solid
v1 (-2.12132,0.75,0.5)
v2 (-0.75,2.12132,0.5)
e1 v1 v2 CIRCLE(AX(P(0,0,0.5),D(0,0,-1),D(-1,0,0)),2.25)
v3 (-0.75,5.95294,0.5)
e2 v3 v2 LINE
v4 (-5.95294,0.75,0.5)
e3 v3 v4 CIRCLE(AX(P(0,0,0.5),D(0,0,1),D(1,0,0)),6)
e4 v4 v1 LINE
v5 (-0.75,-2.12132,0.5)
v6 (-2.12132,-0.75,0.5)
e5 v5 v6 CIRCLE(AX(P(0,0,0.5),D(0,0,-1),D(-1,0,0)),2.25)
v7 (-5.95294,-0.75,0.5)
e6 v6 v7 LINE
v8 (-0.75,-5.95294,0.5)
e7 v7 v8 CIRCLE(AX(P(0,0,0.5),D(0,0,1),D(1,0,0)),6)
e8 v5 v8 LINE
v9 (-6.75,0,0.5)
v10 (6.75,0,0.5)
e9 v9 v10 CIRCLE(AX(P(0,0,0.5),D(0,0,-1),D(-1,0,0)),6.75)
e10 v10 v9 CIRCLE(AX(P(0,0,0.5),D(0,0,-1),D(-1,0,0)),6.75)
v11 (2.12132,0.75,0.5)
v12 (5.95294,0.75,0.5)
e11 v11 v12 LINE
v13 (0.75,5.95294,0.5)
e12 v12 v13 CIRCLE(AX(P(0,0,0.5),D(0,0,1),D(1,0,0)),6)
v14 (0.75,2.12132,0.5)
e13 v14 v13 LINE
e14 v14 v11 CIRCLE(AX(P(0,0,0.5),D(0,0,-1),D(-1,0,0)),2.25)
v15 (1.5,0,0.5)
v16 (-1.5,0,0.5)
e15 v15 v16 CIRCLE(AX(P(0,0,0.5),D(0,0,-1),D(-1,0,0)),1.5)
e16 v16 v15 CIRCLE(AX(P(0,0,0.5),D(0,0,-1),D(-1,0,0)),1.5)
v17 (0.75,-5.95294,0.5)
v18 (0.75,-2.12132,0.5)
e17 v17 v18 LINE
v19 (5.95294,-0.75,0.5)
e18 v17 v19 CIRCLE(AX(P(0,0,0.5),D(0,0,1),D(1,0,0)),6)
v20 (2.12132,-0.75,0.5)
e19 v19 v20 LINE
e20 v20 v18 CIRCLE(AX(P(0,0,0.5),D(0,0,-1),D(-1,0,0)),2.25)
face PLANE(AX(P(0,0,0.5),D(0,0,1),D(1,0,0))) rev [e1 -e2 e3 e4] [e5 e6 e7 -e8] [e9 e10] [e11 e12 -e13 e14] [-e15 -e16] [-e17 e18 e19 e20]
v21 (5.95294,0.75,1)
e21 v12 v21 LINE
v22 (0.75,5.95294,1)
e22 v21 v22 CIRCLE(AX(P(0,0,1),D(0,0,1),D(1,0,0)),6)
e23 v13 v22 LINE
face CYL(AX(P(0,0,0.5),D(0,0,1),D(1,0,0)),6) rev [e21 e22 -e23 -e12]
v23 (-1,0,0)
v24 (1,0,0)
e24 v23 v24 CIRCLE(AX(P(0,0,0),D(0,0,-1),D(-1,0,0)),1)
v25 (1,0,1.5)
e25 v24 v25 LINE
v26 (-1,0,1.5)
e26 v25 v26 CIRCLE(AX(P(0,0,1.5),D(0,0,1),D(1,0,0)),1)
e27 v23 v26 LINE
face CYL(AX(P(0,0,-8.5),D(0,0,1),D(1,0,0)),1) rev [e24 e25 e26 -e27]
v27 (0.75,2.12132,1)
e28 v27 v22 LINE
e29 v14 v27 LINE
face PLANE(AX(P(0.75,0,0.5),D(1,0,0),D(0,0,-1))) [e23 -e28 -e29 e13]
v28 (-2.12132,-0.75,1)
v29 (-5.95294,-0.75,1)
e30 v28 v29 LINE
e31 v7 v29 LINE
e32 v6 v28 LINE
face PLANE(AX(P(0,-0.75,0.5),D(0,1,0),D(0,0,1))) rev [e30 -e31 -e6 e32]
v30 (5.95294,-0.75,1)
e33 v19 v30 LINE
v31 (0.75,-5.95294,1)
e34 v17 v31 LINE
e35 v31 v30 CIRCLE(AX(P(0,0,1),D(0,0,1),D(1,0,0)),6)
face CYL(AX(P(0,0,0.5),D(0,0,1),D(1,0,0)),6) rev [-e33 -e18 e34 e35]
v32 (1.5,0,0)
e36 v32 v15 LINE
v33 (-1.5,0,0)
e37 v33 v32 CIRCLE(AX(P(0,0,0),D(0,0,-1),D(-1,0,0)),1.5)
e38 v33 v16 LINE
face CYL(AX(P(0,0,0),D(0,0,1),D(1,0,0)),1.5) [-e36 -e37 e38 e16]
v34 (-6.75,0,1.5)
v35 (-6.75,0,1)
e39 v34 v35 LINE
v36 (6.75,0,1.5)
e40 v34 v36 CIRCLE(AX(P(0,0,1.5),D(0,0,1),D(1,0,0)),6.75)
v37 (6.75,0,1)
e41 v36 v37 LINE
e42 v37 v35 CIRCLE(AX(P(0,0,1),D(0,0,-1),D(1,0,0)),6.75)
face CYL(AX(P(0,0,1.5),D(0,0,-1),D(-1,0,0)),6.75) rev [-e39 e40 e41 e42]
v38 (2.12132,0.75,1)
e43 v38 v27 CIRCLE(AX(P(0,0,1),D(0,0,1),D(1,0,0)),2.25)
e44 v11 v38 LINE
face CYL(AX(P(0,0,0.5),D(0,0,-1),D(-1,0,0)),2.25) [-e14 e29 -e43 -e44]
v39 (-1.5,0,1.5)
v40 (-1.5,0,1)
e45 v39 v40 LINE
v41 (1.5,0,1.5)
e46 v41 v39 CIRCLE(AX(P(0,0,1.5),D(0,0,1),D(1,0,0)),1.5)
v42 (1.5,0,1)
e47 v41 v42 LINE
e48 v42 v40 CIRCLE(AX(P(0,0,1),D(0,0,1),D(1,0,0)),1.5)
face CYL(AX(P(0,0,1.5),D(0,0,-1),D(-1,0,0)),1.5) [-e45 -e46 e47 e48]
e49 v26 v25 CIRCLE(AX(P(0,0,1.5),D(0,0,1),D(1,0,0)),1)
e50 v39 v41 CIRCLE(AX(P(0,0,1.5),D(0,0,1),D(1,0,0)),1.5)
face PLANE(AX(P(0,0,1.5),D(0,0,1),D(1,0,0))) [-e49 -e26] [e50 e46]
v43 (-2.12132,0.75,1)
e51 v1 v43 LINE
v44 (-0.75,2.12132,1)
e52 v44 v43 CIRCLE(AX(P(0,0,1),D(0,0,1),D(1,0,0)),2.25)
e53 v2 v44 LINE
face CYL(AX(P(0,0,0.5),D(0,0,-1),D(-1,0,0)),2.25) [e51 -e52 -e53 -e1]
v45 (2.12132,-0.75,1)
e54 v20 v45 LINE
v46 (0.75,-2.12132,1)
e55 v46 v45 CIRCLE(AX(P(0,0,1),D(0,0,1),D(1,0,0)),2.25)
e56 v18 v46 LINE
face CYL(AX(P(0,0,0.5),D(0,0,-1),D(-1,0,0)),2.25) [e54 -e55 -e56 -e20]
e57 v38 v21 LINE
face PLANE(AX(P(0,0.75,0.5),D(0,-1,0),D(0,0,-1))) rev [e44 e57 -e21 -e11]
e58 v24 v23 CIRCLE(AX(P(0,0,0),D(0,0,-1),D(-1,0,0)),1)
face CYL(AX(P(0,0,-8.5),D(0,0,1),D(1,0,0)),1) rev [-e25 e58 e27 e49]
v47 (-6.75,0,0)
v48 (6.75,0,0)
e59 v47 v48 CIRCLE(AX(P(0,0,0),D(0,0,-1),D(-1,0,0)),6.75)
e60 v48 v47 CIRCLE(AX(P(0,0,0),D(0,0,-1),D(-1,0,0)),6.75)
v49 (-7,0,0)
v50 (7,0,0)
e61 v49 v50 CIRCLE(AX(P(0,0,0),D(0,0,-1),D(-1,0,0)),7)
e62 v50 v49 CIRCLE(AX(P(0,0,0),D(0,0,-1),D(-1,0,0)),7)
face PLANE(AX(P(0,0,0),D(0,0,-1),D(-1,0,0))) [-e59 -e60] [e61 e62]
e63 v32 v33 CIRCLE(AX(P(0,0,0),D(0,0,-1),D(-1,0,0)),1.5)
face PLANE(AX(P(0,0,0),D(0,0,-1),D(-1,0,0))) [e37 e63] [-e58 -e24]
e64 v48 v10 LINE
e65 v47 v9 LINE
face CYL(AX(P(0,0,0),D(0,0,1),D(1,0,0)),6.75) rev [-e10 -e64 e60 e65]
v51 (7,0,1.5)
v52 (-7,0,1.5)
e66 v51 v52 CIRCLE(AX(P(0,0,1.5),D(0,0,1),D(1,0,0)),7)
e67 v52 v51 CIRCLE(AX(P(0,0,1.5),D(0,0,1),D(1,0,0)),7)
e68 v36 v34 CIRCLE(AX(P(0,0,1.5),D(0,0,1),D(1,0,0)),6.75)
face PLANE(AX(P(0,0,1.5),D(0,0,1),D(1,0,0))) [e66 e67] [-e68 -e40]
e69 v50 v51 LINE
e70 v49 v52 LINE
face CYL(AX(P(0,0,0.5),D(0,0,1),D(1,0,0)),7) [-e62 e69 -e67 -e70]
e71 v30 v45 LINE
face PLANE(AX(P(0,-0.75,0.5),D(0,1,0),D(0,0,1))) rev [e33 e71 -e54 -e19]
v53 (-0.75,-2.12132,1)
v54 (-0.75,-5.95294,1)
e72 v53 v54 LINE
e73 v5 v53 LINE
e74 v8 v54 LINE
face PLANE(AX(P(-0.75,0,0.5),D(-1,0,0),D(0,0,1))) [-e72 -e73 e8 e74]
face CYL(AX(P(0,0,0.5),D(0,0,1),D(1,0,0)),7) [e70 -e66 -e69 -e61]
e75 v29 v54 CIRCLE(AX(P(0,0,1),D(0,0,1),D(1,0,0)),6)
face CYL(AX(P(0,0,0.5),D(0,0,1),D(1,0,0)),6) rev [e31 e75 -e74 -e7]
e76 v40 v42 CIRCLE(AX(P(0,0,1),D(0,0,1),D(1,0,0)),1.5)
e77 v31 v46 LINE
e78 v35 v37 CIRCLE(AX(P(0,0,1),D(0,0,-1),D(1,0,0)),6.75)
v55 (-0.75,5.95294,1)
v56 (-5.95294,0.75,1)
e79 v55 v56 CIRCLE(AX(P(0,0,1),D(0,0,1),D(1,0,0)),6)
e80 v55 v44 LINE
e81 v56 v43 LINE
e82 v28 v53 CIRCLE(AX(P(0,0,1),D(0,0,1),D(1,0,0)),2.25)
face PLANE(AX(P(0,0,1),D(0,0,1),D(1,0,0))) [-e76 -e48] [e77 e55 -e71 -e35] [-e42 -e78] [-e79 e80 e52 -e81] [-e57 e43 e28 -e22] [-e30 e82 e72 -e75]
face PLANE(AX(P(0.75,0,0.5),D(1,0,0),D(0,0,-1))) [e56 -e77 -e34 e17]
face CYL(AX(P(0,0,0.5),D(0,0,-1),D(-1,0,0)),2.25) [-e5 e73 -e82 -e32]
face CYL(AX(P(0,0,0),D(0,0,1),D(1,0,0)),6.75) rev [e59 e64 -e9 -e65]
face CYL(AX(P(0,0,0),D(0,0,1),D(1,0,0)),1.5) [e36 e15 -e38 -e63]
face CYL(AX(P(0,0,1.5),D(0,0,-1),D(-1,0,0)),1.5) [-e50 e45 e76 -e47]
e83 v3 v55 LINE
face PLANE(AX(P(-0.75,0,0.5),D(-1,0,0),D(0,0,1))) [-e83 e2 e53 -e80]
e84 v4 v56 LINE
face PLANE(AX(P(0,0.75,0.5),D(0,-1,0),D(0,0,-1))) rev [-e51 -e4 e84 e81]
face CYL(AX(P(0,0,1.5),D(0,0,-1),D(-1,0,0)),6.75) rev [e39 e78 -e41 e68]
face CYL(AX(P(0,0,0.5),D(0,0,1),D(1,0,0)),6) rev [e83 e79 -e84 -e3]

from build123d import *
from build123d.topology import SkipClean

# Parameters (mm, degrees)
HUB_CORE_SKETCH_R           = 2.25
HUB_CORE_DEPTH              = 0.5
HUB_FLANGE_SKETCH_R         = 6
HUB_FLANGE_6_DEPTH          = 0.5
FRONT_HUB_BOSS_SKETCH_R     = 2.25
FRONT_HUB_BOSS_DEPTH        = 0.5
CROSS_START                 = -0.5
CROSS_SLOT_CUT_DEPTH        = 0.5
WEB_START                   = -0.5
WEB_RING_SKETCH_R           = 6.75
WEB_RING_SKETCH_R_2         = 6
WEB_RING_13_5_DEPTH         = 0.5
FRONT_START                 = -0.5
FRONT_HUB_HOLE_SKETCH_R     = 2.25
FRONT_HUB_HOLE_CUT_DEPTH    = 0.5
BACK_HUB_RECESS_SKETCH_R    = 2.25
BACK_HUB_RECESS_CUT_DEPTH   = 0.5
HUB_RING_A_SKETCH_R         = 1.5
HUB_RING_A_DEPTH            = 0.5
HUB_START                   = 0.5
HUB_RING_B_SKETCH_R         = 1.5
HUB_RING_B_DEPTH            = 0.5
SPOKE_1_DEPTH               = 1.5
SPOKE_1_GROOVE_A_DEPTH      = 0.625
SPOKE_1_GROOVE_B_DEPTH      = 0.625
SPOKE_2_DEPTH               = 1.5
SPOKE_3_DEPTH               = 1.5
SPOKE_4_DEPTH               = 1.5
SPOKE_GROOVES_A_DEPTH       = 0.65
SPOKE_GROOVES_B_DEPTH       = 0.65
CROSS_SPOKES_DEPTH          = 1.5
CROSS_SPOKES_2_DEPTH        = 1.5
CROSS_SPOKES_3_DEPTH        = 1.5
CROSS_SPOKES_4_DEPTH        = 1.5
CROSS_SPOKE_GROOVES_A_DEPTH = 0.625
CROSS_SPOKE_GROOVES_B_DEPTH = 0.625
CENTRE_HOLE_SKETCH_R        = 1
CENTRE_HOLE_CUT_DEPTH       = 10
RIM_START                   = -0.5
RIM_RING_1_SKETCH_R         = 7
RIM_RING_1_SKETCH_R_2       = 6.75
RIM_RING_1_14_DEPTH         = 0.5
RIM_RING_2_SKETCH_R         = 7
RIM_RING_2_SKETCH_R_2       = 6.75
RIM_RING_2_14_DEPTH         = 0.5
RIM_START_2                 = 0.5
RIM_RING_3_SKETCH_R         = 7
RIM_RING_3_SKETCH_R_2       = 6.75
RIM_RING_3_14_DEPTH         = 0.5


with BuildPart() as part:
    # Hub Core Sketch → Hub Core (new body)
    with BuildSketch(Plane.XY):
        Circle(HUB_CORE_SKETCH_R)
    extrude(amount=HUB_CORE_DEPTH)

    # Hub Flange Sketch → Hub Flange Ø6 (add)
    with BuildSketch(Plane.XY.offset(0.5)):
        Circle(HUB_FLANGE_SKETCH_R)
    extrude(amount=HUB_FLANGE_6_DEPTH)

    # Front Hub Boss Sketch → Front Hub Boss (add)
    with BuildSketch(Plane.XY.offset(1)):
        Circle(FRONT_HUB_BOSS_SKETCH_R)
    extrude(amount=FRONT_HUB_BOSS_DEPTH)

    # Cross Slot Sketch → Cross Slot Cut (cut)
    with SkipClean():  # the faces are left unmerged after this step: merging them gives an invalid solid
        with BuildSketch(Plane.XY.offset(1).offset(CROSS_START)):
            with BuildLine():
                ThreePointArc((-2.121320344, 0.75), (-1.590990258, 1.590990258), (-0.75, 2.121320344))
                Line((-0.75, 2.121320344), (-0.75, 5.95294045))
                ThreePointArc((-0.75, 5.95294045), (-4.242640687, 4.242640687), (-5.95294045, 0.75))
                Line((-5.95294045, 0.75), (-2.121320344, 0.75))
            make_face()
            with BuildLine():
                Line((0.75, 5.95294045), (0.75, 2.121320344))
                ThreePointArc((0.75, 2.121320344), (1.590990258, 1.590990258), (2.121320344, 0.75))
                Line((2.121320344, 0.75), (5.95294045, 0.75))
                ThreePointArc((5.95294045, 0.75), (4.242640687, 4.242640687), (0.75, 5.95294045))
            make_face()
            with BuildLine():
                ThreePointArc((2.121320344, -0.75), (1.590990258, -1.590990258), (0.75, -2.121320344))
                Line((0.75, -2.121320344), (0.75, -5.95294045))
                ThreePointArc((0.75, -5.95294045), (4.242640687, -4.242640687), (5.95294045, -0.75))
                Line((5.95294045, -0.75), (2.121320344, -0.75))
            make_face()
            with BuildLine():
                Line((-0.75, -5.95294045), (-0.75, -2.121320344))
                ThreePointArc((-0.75, -2.121320344), (-1.590990258, -1.590990258), (-2.121320344, -0.75))
                Line((-2.121320344, -0.75), (-5.95294045, -0.75))
                ThreePointArc((-5.95294045, -0.75), (-4.242640687, -4.242640687), (-0.75, -5.95294045))
            make_face()
        extrude(amount=CROSS_SLOT_CUT_DEPTH, mode=Mode.SUBTRACT)

    # Web Ring Sketch → Web Ring Ø13.5 (add)
    with SkipClean():  # the faces are left unmerged after this step: merging them gives an invalid solid
        with BuildSketch(Plane.XY.offset(1).offset(WEB_START)):
            Circle(WEB_RING_SKETCH_R)
            Circle(WEB_RING_SKETCH_R_2, mode=Mode.SUBTRACT)
        extrude(amount=WEB_RING_13_5_DEPTH)

    # Front Hub Hole Sketch → Front Hub Hole Cut (cut)
    with SkipClean():  # the faces are left unmerged after this step: merging them gives an invalid solid
        with BuildSketch(Plane.XY.offset(1.5).offset(FRONT_START)):
            with Locations(Location((0, 0, 0), (0, 0, 199.471220634))):
                Circle(FRONT_HUB_HOLE_SKETCH_R)
        extrude(amount=FRONT_HUB_HOLE_CUT_DEPTH, mode=Mode.SUBTRACT)

    # Back Hub Recess Sketch → Back Hub Recess Cut (cut)
    with BuildSketch(Plane(origin=(0, 0, 0), x_dir=(-1, 0, 0), z_dir=(0, 0, -1))):
        Circle(BACK_HUB_RECESS_SKETCH_R)
    extrude(amount=-BACK_HUB_RECESS_CUT_DEPTH, mode=Mode.SUBTRACT)

    # Hub Ring A Sketch → Hub Ring A (add)
    with BuildSketch(Plane(origin=(0, 0, 0.5), x_dir=(-1, 0, 0), z_dir=(0, 0, -1))):
        Circle(HUB_RING_A_SKETCH_R)
    extrude(amount=HUB_RING_A_DEPTH)

    # Hub Ring B Sketch → Hub Ring B (add)
    with BuildSketch(Plane.XY.offset(1).offset(HUB_START)):
        with Locations(Location((0, 0, 0), (0, 0, 180))):
            Circle(HUB_RING_B_SKETCH_R)
    extrude(amount=-HUB_RING_B_DEPTH)

    # Centre Hole Sketch → Centre Hole Cut (cut)
    with BuildSketch(Plane.XY.offset(1.5)):
        Circle(CENTRE_HOLE_SKETCH_R)
    extrude(amount=-CENTRE_HOLE_CUT_DEPTH, mode=Mode.SUBTRACT)

    # Rim Ring 1 Sketch → Rim Ring 1 Ø14 (add)
    with BuildSketch(Plane.XY.offset(1).offset(RIM_START)):
        Circle(RIM_RING_1_SKETCH_R)
        Circle(RIM_RING_1_SKETCH_R_2, mode=Mode.SUBTRACT)
    extrude(amount=RIM_RING_1_14_DEPTH)

    # Rim Ring 2 Sketch → Rim Ring 2 Ø14 (add)
    with BuildSketch(Plane.XY.offset(1)):
        Circle(RIM_RING_2_SKETCH_R)
        Circle(RIM_RING_2_SKETCH_R_2, mode=Mode.SUBTRACT)
    extrude(amount=RIM_RING_2_14_DEPTH)

    # Rim Ring 3 Sketch → Rim Ring 3 Ø14 (add)
    with BuildSketch(Plane(origin=(0, 0, 0.5), x_dir=(-1, 0, 0), z_dir=(0, 0, -1)).offset(RIM_START_2)):
        with Locations(Location((0, 0, 0), (0, 0, 180))):
            Circle(RIM_RING_3_SKETCH_R)
        with Locations(Location((0, 0, 0), (0, 0, 180))):
            Circle(RIM_RING_3_SKETCH_R_2, mode=Mode.SUBTRACT)
    extrude(amount=-RIM_RING_3_14_DEPTH)


with BuildPart() as body_2:
    # Spoke 1 Sketch → Spoke 1 (new body)
    with BuildSketch(Plane.XZ.offset(0.75)):
        Polygon((-1.5, 1.5), (-1.5, 1), (-6.75, 1), (-5.25, 1.5), align=None)
    extrude(amount=-SPOKE_1_DEPTH)

    # Spoke 1 Groove A Sketch → Spoke 1 Groove A (cut)
    with BuildSketch(Plane.XZ.offset(0.75)):
        Polygon((-6.75, 1), (-5.25, 1.5), (-1.5, 1.5), (-1.5, 1), align=None)
    extrude(amount=-SPOKE_1_GROOVE_A_DEPTH, mode=Mode.SUBTRACT)

    # Spoke 1 Groove B Sketch → Spoke 1 Groove B (cut)
    with BuildSketch(Plane(origin=(0, 0.75, 0), x_dir=(1, 0, 0), z_dir=(0, 1, 0))):
        Polygon((-1.5, -1.5), (-1.5, -1), (-6.75, -1), (-5.25, -1.5), align=None)
    extrude(amount=-SPOKE_1_GROOVE_B_DEPTH, mode=Mode.SUBTRACT)


with BuildPart() as body_3:
    # Spoke 2 Sketch → Spoke 2 (new body)
    with BuildSketch(Plane.XZ.offset(0.75)):
        Polygon((5.25, 1.5), (1.5, 1.5), (1.5, 1), (2.121320344, 1), (5.95294045, 1), (6.75, 1), align=None)
    extrude(amount=-SPOKE_2_DEPTH)


with BuildPart() as body_4:
    # Spoke 3 Sketch → Spoke 3 (new body)
    with BuildSketch(Plane.XZ.offset(0.75)):
        Polygon((1.5, 0), (1.5, 0.5), (6.75, 0.5), (5.25, 0), align=None)
    extrude(amount=-SPOKE_3_DEPTH)


with BuildPart() as body_5:
    # Spoke 4 Sketch → Spoke 4 (new body)
    with BuildSketch(Plane.XZ.offset(0.75)):
        Polygon((-1.5, 0), (-5.25, 0), (-6.75, 0.5), (-1.5, 0.5), align=None)
    extrude(amount=-SPOKE_4_DEPTH)


with BuildPart() as spoke_grooves_a_tool:
    # Spoke Grooves A Sketch → Spoke Grooves A (new body)
    with BuildSketch(Plane.XZ.offset(0.75)):
        Polygon((1.5, 1.5), (1.5, 1), (6.75, 1), (5.25, 1.5), align=None)
        Polygon((1.5, 0), (1.5, 0.5), (6.75, 0.5), (5.25, 0), align=None)
        Polygon((-6.75, 0.5), (-1.5, 0.5), (-1.5, 0), (-5.25, 0), align=None)
    extrude(amount=-SPOKE_GROOVES_A_DEPTH)


with BuildPart() as body_3_1:
    add(body_3.part)

    # Spoke Grooves A: cut by spoke_grooves_a_tool
    add(spoke_grooves_a_tool.part, mode=Mode.SUBTRACT)


with BuildPart() as body_4_1:
    add(body_4.part)

    # Spoke Grooves A: cut by spoke_grooves_a_tool
    add(spoke_grooves_a_tool.part, mode=Mode.SUBTRACT)


with BuildPart() as body_5_1:
    add(body_5.part)

    # Spoke Grooves A: cut by spoke_grooves_a_tool
    add(spoke_grooves_a_tool.part, mode=Mode.SUBTRACT)


with BuildPart() as spoke_grooves_b_tool:
    # Spoke Grooves B Sketch → Spoke Grooves B (new body)
    with BuildSketch(Plane(origin=(0, 0.75, 0), x_dir=(1, 0, 0), z_dir=(0, 1, 0))):
        Polygon((1.5, 0), (5.25, 0), (6.75, -0.5), (1.5, -0.5), align=None)
        Polygon((1.5, -1.5), (1.5, -1), (6.75, -1), (5.25, -1.5), align=None)
        Polygon((-6.75, -0.5), (-1.5, -0.5), (-1.5, 0), (-5.25, 0), align=None)
    extrude(amount=-SPOKE_GROOVES_B_DEPTH)


with BuildPart() as body_3_2:
    add(body_3_1.part)

    # Spoke Grooves B: cut by spoke_grooves_b_tool
    add(spoke_grooves_b_tool.part, mode=Mode.SUBTRACT)


with BuildPart() as body_4_2:
    add(body_4_1.part)

    # Spoke Grooves B: cut by spoke_grooves_b_tool
    add(spoke_grooves_b_tool.part, mode=Mode.SUBTRACT)


with BuildPart() as body_5_2:
    add(body_5_1.part)

    # Spoke Grooves B: cut by spoke_grooves_b_tool
    add(spoke_grooves_b_tool.part, mode=Mode.SUBTRACT)


with BuildPart() as body_6:
    # Cross Spokes Sketch → Cross Spokes (new body)
    with BuildSketch(Plane.ZY.offset(0.75)):
        Polygon((1, 1.5), (1, 6.75), (1.5, 5.25), (1.5, 1.5), align=None)
    extrude(amount=-CROSS_SPOKES_DEPTH)


with BuildPart() as body_7:
    # Cross Spokes Sketch → Cross Spokes 2 (new body)
    with BuildSketch(Plane.ZY.offset(0.75)):
        Polygon((0.5, 1.5), (0.5, 6.75), (0, 5.25), (0, 1.5), align=None)
    extrude(amount=-CROSS_SPOKES_2_DEPTH)


with BuildPart() as body_8:
    # Cross Spokes Sketch → Cross Spokes 3 (new body)
    with BuildSketch(Plane.ZY.offset(0.75)):
        Polygon((1, -1.5), (1, -6.75), (1.5, -5.25), (1.5, -1.5), align=None)
    extrude(amount=-CROSS_SPOKES_3_DEPTH)


with BuildPart() as body_9:
    # Cross Spokes Sketch → Cross Spokes 4 (new body)
    with BuildSketch(Plane.ZY.offset(0.75)):
        Polygon((0.5, -1.5), (0.5, -6.75), (0, -5.25), (0, -1.5), align=None)
    extrude(amount=-CROSS_SPOKES_4_DEPTH)


with BuildPart() as cross_spoke_grooves_a_tool:
    # Cross Spoke Grooves A Sketch → Cross Spoke Grooves A (new body)
    with BuildSketch(Plane.ZY.offset(0.75)):
        Polygon((1.5, 1.5), (1, 1.5), (1, 6.75), (1.5, 5.25), align=None)
        Polygon((0.5, 6.75), (0.5, 1.5), (0, 1.5), (0, 5.25), align=None)
        Polygon((1, -6.75), (1, -1.5), (1.5, -1.5), (1.5, -5.25), align=None)
        Polygon((0, -1.5), (0.5, -1.5), (0.5, -6.75), (0, -5.25), align=None)
    extrude(amount=-CROSS_SPOKE_GROOVES_A_DEPTH)


with BuildPart() as body_6_1:
    add(body_6.part)

    # Cross Spoke Grooves A: cut by cross_spoke_grooves_a_tool
    add(cross_spoke_grooves_a_tool.part, mode=Mode.SUBTRACT)


with BuildPart() as body_7_1:
    add(body_7.part)

    # Cross Spoke Grooves A: cut by cross_spoke_grooves_a_tool
    add(cross_spoke_grooves_a_tool.part, mode=Mode.SUBTRACT)


with BuildPart() as body_8_1:
    add(body_8.part)

    # Cross Spoke Grooves A: cut by cross_spoke_grooves_a_tool
    add(cross_spoke_grooves_a_tool.part, mode=Mode.SUBTRACT)


with BuildPart() as body_9_1:
    add(body_9.part)

    # Cross Spoke Grooves A: cut by cross_spoke_grooves_a_tool
    add(cross_spoke_grooves_a_tool.part, mode=Mode.SUBTRACT)


with BuildPart() as cross_spoke_grooves_b_tool:
    # Cross Spoke Grooves B Sketch → Cross Spoke Grooves B (new body)
    with BuildSketch(Plane(origin=(0.75, 0, 0), x_dir=(0, 0, -1), z_dir=(1, 0, 0))):
        Polygon((0, 1.5), (-0.5, 1.5), (-0.5, 6.75), (0, 5.25), align=None)
        Polygon((-1, 6.75), (-1, 1.5), (-1.5, 1.5), (-1.5, 5.25), align=None)
        Polygon((0, -1.5), (0, -5.25), (-0.5, -6.75), (-0.5, -1.5), align=None)
        Polygon((-1.5, -1.5), (-1.5, -5.25), (-1, -6.75), (-1, -1.5), align=None)
    extrude(amount=-CROSS_SPOKE_GROOVES_B_DEPTH)


with BuildPart() as body_6_2:
    add(body_6_1.part)

    # Cross Spoke Grooves B: cut by cross_spoke_grooves_b_tool
    add(cross_spoke_grooves_b_tool.part, mode=Mode.SUBTRACT)


with BuildPart() as body_7_2:
    add(body_7_1.part)

    # Cross Spoke Grooves B: cut by cross_spoke_grooves_b_tool
    add(cross_spoke_grooves_b_tool.part, mode=Mode.SUBTRACT)


with BuildPart() as body_8_2:
    add(body_8_1.part)

    # Cross Spoke Grooves B: cut by cross_spoke_grooves_b_tool
    add(cross_spoke_grooves_b_tool.part, mode=Mode.SUBTRACT)


with BuildPart() as body_9_2:
    add(body_9_1.part)

    # Cross Spoke Grooves B: cut by cross_spoke_grooves_b_tool
    add(cross_spoke_grooves_b_tool.part, mode=Mode.SUBTRACT)


solid = part.part
